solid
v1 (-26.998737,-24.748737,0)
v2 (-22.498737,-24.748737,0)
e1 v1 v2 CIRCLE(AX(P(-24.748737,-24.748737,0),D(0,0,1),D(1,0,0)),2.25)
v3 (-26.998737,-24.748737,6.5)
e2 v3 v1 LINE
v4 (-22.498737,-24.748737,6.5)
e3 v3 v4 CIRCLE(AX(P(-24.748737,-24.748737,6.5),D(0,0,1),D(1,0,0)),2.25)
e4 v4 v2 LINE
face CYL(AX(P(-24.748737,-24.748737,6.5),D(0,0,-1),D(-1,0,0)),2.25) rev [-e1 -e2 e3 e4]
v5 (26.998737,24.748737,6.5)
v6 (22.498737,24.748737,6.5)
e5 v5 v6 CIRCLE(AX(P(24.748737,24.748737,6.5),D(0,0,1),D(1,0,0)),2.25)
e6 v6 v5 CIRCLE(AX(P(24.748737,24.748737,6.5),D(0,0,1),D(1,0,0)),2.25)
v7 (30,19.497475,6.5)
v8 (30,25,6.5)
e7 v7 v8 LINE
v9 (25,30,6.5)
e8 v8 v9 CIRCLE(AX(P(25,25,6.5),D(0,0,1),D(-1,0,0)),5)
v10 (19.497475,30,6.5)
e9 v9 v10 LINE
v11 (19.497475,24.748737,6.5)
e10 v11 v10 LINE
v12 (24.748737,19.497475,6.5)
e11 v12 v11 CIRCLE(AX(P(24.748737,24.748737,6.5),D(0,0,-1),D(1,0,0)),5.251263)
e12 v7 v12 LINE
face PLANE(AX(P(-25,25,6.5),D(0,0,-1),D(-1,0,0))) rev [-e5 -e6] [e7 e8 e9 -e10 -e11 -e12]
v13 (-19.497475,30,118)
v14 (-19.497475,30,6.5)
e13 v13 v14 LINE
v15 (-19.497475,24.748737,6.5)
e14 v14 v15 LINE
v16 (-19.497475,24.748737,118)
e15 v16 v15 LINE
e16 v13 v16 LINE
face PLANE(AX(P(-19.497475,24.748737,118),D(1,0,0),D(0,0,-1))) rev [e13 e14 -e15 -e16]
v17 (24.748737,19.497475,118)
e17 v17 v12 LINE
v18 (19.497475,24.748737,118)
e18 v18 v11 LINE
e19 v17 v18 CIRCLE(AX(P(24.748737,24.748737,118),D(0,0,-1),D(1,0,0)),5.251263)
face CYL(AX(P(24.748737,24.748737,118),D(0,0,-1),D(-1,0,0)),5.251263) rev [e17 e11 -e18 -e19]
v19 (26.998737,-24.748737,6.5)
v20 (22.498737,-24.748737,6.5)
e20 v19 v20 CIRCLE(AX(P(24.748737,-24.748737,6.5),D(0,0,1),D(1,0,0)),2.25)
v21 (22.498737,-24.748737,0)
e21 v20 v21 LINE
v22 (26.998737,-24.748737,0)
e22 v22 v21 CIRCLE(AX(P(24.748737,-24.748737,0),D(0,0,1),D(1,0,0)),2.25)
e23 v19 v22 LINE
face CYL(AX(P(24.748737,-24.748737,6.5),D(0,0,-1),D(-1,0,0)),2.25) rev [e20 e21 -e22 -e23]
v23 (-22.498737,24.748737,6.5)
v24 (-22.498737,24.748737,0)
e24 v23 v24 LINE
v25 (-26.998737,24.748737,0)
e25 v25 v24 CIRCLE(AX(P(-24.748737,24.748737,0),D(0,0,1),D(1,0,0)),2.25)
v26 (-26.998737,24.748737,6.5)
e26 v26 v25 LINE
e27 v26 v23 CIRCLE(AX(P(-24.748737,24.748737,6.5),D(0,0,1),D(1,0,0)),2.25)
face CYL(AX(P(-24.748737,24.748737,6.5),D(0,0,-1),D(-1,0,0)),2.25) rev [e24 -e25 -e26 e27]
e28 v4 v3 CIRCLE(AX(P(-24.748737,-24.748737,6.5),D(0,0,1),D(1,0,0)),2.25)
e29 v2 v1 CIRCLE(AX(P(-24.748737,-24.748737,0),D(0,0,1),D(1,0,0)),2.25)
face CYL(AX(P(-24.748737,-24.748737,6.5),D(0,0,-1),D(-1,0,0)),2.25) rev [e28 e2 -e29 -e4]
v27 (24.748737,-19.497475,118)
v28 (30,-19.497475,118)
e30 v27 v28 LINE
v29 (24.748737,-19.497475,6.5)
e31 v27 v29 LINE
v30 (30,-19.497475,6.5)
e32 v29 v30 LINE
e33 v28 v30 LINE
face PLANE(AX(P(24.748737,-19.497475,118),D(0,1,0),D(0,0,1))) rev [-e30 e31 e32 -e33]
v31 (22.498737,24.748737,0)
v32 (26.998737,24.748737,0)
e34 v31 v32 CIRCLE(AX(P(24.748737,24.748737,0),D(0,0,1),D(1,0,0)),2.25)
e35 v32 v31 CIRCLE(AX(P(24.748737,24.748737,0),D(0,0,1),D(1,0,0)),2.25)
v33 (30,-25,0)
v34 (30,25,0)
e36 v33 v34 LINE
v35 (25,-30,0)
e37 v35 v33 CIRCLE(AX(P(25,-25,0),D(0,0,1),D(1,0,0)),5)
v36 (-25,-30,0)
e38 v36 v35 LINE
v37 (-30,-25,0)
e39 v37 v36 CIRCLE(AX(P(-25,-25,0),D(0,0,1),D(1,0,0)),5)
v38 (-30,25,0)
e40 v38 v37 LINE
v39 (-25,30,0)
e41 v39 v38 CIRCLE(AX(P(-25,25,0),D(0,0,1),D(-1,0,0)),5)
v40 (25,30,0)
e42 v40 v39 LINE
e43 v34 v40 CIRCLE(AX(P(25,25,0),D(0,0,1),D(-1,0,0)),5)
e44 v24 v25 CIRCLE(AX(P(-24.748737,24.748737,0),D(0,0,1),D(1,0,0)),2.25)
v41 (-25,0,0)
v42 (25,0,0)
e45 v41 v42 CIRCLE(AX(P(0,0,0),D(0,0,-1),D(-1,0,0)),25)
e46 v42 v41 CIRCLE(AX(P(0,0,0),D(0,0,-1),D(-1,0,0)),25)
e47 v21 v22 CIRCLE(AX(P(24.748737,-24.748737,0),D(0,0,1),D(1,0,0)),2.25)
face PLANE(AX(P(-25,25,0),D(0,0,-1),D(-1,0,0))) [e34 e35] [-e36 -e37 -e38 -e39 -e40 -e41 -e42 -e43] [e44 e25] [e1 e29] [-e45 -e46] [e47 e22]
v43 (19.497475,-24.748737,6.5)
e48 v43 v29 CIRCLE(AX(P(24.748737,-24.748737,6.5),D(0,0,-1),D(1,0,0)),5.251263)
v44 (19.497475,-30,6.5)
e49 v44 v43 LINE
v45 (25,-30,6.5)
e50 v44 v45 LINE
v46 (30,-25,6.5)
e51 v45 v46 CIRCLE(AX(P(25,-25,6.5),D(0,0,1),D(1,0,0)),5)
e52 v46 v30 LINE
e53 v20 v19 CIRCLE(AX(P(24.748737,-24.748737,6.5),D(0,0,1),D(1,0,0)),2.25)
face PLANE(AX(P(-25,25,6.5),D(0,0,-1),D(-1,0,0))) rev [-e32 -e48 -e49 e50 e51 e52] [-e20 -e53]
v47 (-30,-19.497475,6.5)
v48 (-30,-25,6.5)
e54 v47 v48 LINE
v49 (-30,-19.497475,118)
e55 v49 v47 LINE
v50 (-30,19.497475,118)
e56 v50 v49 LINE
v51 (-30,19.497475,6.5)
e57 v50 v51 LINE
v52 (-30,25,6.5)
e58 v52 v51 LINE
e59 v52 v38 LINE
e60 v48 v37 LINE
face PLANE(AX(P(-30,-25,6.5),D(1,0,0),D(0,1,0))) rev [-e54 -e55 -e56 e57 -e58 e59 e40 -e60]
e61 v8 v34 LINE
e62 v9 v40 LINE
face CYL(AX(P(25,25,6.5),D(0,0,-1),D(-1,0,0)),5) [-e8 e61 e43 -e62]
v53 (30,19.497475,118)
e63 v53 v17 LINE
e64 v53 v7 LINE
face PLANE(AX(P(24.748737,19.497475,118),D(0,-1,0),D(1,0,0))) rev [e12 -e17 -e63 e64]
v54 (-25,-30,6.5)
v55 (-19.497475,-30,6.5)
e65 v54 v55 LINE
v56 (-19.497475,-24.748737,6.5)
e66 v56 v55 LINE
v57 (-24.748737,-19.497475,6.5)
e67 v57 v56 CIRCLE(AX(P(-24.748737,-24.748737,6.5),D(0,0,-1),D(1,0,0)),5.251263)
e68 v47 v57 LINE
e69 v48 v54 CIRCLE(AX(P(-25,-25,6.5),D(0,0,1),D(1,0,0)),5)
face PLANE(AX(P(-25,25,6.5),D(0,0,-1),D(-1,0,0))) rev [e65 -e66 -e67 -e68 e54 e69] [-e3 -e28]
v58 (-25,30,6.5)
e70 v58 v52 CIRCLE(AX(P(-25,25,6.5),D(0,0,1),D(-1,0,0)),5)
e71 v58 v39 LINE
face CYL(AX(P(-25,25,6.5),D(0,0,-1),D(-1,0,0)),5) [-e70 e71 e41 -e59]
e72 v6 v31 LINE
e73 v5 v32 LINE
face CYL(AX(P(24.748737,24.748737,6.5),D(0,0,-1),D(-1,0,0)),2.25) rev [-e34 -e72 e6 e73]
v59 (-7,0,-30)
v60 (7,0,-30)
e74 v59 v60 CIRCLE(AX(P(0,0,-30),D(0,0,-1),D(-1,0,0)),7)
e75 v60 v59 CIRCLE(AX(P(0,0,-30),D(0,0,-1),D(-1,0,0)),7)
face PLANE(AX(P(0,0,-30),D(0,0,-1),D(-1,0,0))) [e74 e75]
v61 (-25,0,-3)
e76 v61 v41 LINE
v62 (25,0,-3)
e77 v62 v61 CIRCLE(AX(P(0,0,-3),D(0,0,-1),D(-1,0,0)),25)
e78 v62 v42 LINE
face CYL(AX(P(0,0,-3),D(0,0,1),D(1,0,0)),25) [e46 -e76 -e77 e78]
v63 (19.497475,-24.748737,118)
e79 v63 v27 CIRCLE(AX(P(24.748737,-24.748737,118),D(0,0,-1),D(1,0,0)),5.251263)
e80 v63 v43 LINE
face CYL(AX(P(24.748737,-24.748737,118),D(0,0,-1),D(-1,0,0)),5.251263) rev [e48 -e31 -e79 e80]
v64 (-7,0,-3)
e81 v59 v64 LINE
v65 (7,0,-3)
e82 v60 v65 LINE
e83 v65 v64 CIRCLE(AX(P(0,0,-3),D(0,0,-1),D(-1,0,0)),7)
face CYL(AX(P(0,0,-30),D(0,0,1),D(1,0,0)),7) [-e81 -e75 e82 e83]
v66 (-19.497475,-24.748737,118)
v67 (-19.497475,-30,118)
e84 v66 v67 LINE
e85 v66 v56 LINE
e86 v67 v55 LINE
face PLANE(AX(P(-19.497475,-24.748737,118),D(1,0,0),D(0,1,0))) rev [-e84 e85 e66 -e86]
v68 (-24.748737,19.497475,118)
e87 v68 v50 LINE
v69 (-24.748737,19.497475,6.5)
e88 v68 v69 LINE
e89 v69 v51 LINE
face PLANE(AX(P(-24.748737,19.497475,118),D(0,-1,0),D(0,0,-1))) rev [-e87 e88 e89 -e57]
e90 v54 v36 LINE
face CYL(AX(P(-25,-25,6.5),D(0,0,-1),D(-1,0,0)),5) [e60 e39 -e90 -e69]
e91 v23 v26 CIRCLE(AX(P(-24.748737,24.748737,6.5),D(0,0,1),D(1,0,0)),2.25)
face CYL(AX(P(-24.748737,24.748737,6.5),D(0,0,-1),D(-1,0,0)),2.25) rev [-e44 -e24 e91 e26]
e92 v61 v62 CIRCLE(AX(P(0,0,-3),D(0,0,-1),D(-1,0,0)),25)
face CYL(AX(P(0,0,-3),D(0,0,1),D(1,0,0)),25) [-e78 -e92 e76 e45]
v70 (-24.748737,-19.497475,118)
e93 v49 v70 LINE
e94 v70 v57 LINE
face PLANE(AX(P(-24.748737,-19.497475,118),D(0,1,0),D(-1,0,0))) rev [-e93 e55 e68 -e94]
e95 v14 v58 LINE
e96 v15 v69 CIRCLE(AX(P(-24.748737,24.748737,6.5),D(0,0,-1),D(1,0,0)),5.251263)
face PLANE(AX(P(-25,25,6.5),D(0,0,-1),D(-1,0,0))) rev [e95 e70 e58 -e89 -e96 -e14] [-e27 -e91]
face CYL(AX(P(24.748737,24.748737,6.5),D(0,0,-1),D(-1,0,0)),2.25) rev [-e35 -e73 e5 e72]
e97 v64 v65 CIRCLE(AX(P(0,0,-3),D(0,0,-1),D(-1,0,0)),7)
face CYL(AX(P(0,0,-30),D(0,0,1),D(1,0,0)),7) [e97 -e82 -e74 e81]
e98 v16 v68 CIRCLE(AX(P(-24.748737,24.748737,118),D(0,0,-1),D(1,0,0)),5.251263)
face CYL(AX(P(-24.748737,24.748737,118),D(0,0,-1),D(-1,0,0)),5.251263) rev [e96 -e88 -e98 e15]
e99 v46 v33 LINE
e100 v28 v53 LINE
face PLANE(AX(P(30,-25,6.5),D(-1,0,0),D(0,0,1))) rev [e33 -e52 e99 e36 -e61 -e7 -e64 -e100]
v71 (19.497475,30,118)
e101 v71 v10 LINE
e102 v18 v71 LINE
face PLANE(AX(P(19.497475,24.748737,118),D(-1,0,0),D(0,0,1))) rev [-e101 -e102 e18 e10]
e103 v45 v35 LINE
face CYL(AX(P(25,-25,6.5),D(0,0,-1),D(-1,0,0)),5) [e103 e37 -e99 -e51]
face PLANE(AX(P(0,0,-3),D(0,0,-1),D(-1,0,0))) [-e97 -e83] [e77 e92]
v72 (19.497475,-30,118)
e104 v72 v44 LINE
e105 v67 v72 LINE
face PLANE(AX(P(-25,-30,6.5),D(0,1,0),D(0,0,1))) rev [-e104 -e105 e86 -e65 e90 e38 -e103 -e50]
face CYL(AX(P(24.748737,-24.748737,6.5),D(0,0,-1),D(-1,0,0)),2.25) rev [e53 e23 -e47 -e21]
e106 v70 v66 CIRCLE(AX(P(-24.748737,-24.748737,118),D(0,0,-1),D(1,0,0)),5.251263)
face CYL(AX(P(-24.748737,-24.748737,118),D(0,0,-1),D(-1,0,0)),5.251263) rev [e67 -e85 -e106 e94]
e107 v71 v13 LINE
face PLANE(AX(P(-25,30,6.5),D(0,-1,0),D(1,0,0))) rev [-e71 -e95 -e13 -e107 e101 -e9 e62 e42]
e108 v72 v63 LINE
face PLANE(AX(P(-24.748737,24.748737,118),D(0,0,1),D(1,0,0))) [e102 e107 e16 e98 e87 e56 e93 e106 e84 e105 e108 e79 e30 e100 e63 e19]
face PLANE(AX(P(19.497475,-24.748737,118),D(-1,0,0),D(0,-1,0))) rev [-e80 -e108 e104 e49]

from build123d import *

# Parameters (mm, degrees)
SKETCH1_R      = 2.25
EXTRUDE1_DEPTH = 6.5
EXTRUDE2_DEPTH = 111.5
SKETCH3_R      = 25
EXTRUDE3_DEPTH = 3
SKETCH4_R      = 7
EXTRUDE4_DEPTH = 27


with BuildPart() as part:
    # Sketch1 → Extrude1 (new body)
    with BuildSketch(Plane.XY):
        with BuildLine():
            Line((-25, -30), (25, -30))
            ThreePointArc((25, -30), (28.535533906, -28.535533906), (30, -25))
            Line((30, -25), (30, 25))
            ThreePointArc((30, 25), (28.535533906, 28.535533906), (25, 30))
            Line((25, 30), (-25, 30))
            ThreePointArc((-25, 30), (-28.535533906, 28.535533906), (-30, 25))
            Line((-30, 25), (-30, -25))
            ThreePointArc((-30, -25), (-28.535533906, -28.535533906), (-25, -30))
        make_face()
        with Locations(Location((-24.748737342, 24.748737342, 0), (0, 0, 180))):
            Circle(SKETCH1_R, mode=Mode.SUBTRACT)
        with Locations(Location((-24.748737342, -24.748737342, 0), (0, 0, 180))):
            Circle(SKETCH1_R, mode=Mode.SUBTRACT)
        with Locations(Location((24.748737342, -24.748737342, 0), (0, 0, 180))):
            Circle(SKETCH1_R, mode=Mode.SUBTRACT)
        with Locations(Location((24.748737342, 24.748737342, 0), (0, 0, 180))):
            Circle(SKETCH1_R, mode=Mode.SUBTRACT)
    extrude(amount=EXTRUDE1_DEPTH)

    # Sketch2 → Extrude2 (add)
    with BuildSketch(Plane.XY.offset(6.5)):
        with BuildLine():
            Line((-19.497474683, -30), (19.497474683, -30))
            Line((19.497474683, -30), (19.497474683, -24.748737342))
            ThreePointArc((19.497474683, -24.748737342), (21.035533906, -21.035533906), (24.748737342, -19.497474683))
            Line((24.748737342, -19.497474683), (30, -19.497474683))
            Line((30, -19.497474683), (30, 19.497474683))
            Line((30, 19.497474683), (24.748737342, 19.497474683))
            ThreePointArc((24.748737342, 19.497474683), (21.035533906, 21.035533906), (19.497474683, 24.748737342))
            Line((19.497474683, 24.748737342), (19.497474683, 30))
            Line((19.497474683, 30), (-19.497474683, 30))
            Line((-19.497474683, 30), (-19.497474683, 24.748737342))
            ThreePointArc((-19.497474683, 24.748737342), (-21.035533906, 21.035533906), (-24.748737342, 19.497474683))
            Line((-24.748737342, 19.497474683), (-30, 19.497474683))
            Line((-30, 19.497474683), (-30, -19.497474683))
            Line((-30, -19.497474683), (-24.748737342, -19.497474683))
            ThreePointArc((-24.748737342, -19.497474683), (-21.035533906, -21.035533906), (-19.497474683, -24.748737342))
            Line((-19.497474683, -24.748737342), (-19.497474683, -30))
        make_face()
    extrude(amount=EXTRUDE2_DEPTH)

    # Sketch3 → Extrude3 (add)
    with BuildSketch(Plane(origin=(0, 0, 0), x_dir=(-1, 0, 0), z_dir=(0, 0, -1))):
        Circle(SKETCH3_R)
    extrude(amount=EXTRUDE3_DEPTH)

    # Sketch4 → Extrude4 (add)
    with BuildSketch(Plane(origin=(0, 0, -3), x_dir=(-1, 0, 0), z_dir=(0, 0, -1))):
        Circle(SKETCH4_R)
    extrude(amount=EXTRUDE4_DEPTH)


solid = part.part
